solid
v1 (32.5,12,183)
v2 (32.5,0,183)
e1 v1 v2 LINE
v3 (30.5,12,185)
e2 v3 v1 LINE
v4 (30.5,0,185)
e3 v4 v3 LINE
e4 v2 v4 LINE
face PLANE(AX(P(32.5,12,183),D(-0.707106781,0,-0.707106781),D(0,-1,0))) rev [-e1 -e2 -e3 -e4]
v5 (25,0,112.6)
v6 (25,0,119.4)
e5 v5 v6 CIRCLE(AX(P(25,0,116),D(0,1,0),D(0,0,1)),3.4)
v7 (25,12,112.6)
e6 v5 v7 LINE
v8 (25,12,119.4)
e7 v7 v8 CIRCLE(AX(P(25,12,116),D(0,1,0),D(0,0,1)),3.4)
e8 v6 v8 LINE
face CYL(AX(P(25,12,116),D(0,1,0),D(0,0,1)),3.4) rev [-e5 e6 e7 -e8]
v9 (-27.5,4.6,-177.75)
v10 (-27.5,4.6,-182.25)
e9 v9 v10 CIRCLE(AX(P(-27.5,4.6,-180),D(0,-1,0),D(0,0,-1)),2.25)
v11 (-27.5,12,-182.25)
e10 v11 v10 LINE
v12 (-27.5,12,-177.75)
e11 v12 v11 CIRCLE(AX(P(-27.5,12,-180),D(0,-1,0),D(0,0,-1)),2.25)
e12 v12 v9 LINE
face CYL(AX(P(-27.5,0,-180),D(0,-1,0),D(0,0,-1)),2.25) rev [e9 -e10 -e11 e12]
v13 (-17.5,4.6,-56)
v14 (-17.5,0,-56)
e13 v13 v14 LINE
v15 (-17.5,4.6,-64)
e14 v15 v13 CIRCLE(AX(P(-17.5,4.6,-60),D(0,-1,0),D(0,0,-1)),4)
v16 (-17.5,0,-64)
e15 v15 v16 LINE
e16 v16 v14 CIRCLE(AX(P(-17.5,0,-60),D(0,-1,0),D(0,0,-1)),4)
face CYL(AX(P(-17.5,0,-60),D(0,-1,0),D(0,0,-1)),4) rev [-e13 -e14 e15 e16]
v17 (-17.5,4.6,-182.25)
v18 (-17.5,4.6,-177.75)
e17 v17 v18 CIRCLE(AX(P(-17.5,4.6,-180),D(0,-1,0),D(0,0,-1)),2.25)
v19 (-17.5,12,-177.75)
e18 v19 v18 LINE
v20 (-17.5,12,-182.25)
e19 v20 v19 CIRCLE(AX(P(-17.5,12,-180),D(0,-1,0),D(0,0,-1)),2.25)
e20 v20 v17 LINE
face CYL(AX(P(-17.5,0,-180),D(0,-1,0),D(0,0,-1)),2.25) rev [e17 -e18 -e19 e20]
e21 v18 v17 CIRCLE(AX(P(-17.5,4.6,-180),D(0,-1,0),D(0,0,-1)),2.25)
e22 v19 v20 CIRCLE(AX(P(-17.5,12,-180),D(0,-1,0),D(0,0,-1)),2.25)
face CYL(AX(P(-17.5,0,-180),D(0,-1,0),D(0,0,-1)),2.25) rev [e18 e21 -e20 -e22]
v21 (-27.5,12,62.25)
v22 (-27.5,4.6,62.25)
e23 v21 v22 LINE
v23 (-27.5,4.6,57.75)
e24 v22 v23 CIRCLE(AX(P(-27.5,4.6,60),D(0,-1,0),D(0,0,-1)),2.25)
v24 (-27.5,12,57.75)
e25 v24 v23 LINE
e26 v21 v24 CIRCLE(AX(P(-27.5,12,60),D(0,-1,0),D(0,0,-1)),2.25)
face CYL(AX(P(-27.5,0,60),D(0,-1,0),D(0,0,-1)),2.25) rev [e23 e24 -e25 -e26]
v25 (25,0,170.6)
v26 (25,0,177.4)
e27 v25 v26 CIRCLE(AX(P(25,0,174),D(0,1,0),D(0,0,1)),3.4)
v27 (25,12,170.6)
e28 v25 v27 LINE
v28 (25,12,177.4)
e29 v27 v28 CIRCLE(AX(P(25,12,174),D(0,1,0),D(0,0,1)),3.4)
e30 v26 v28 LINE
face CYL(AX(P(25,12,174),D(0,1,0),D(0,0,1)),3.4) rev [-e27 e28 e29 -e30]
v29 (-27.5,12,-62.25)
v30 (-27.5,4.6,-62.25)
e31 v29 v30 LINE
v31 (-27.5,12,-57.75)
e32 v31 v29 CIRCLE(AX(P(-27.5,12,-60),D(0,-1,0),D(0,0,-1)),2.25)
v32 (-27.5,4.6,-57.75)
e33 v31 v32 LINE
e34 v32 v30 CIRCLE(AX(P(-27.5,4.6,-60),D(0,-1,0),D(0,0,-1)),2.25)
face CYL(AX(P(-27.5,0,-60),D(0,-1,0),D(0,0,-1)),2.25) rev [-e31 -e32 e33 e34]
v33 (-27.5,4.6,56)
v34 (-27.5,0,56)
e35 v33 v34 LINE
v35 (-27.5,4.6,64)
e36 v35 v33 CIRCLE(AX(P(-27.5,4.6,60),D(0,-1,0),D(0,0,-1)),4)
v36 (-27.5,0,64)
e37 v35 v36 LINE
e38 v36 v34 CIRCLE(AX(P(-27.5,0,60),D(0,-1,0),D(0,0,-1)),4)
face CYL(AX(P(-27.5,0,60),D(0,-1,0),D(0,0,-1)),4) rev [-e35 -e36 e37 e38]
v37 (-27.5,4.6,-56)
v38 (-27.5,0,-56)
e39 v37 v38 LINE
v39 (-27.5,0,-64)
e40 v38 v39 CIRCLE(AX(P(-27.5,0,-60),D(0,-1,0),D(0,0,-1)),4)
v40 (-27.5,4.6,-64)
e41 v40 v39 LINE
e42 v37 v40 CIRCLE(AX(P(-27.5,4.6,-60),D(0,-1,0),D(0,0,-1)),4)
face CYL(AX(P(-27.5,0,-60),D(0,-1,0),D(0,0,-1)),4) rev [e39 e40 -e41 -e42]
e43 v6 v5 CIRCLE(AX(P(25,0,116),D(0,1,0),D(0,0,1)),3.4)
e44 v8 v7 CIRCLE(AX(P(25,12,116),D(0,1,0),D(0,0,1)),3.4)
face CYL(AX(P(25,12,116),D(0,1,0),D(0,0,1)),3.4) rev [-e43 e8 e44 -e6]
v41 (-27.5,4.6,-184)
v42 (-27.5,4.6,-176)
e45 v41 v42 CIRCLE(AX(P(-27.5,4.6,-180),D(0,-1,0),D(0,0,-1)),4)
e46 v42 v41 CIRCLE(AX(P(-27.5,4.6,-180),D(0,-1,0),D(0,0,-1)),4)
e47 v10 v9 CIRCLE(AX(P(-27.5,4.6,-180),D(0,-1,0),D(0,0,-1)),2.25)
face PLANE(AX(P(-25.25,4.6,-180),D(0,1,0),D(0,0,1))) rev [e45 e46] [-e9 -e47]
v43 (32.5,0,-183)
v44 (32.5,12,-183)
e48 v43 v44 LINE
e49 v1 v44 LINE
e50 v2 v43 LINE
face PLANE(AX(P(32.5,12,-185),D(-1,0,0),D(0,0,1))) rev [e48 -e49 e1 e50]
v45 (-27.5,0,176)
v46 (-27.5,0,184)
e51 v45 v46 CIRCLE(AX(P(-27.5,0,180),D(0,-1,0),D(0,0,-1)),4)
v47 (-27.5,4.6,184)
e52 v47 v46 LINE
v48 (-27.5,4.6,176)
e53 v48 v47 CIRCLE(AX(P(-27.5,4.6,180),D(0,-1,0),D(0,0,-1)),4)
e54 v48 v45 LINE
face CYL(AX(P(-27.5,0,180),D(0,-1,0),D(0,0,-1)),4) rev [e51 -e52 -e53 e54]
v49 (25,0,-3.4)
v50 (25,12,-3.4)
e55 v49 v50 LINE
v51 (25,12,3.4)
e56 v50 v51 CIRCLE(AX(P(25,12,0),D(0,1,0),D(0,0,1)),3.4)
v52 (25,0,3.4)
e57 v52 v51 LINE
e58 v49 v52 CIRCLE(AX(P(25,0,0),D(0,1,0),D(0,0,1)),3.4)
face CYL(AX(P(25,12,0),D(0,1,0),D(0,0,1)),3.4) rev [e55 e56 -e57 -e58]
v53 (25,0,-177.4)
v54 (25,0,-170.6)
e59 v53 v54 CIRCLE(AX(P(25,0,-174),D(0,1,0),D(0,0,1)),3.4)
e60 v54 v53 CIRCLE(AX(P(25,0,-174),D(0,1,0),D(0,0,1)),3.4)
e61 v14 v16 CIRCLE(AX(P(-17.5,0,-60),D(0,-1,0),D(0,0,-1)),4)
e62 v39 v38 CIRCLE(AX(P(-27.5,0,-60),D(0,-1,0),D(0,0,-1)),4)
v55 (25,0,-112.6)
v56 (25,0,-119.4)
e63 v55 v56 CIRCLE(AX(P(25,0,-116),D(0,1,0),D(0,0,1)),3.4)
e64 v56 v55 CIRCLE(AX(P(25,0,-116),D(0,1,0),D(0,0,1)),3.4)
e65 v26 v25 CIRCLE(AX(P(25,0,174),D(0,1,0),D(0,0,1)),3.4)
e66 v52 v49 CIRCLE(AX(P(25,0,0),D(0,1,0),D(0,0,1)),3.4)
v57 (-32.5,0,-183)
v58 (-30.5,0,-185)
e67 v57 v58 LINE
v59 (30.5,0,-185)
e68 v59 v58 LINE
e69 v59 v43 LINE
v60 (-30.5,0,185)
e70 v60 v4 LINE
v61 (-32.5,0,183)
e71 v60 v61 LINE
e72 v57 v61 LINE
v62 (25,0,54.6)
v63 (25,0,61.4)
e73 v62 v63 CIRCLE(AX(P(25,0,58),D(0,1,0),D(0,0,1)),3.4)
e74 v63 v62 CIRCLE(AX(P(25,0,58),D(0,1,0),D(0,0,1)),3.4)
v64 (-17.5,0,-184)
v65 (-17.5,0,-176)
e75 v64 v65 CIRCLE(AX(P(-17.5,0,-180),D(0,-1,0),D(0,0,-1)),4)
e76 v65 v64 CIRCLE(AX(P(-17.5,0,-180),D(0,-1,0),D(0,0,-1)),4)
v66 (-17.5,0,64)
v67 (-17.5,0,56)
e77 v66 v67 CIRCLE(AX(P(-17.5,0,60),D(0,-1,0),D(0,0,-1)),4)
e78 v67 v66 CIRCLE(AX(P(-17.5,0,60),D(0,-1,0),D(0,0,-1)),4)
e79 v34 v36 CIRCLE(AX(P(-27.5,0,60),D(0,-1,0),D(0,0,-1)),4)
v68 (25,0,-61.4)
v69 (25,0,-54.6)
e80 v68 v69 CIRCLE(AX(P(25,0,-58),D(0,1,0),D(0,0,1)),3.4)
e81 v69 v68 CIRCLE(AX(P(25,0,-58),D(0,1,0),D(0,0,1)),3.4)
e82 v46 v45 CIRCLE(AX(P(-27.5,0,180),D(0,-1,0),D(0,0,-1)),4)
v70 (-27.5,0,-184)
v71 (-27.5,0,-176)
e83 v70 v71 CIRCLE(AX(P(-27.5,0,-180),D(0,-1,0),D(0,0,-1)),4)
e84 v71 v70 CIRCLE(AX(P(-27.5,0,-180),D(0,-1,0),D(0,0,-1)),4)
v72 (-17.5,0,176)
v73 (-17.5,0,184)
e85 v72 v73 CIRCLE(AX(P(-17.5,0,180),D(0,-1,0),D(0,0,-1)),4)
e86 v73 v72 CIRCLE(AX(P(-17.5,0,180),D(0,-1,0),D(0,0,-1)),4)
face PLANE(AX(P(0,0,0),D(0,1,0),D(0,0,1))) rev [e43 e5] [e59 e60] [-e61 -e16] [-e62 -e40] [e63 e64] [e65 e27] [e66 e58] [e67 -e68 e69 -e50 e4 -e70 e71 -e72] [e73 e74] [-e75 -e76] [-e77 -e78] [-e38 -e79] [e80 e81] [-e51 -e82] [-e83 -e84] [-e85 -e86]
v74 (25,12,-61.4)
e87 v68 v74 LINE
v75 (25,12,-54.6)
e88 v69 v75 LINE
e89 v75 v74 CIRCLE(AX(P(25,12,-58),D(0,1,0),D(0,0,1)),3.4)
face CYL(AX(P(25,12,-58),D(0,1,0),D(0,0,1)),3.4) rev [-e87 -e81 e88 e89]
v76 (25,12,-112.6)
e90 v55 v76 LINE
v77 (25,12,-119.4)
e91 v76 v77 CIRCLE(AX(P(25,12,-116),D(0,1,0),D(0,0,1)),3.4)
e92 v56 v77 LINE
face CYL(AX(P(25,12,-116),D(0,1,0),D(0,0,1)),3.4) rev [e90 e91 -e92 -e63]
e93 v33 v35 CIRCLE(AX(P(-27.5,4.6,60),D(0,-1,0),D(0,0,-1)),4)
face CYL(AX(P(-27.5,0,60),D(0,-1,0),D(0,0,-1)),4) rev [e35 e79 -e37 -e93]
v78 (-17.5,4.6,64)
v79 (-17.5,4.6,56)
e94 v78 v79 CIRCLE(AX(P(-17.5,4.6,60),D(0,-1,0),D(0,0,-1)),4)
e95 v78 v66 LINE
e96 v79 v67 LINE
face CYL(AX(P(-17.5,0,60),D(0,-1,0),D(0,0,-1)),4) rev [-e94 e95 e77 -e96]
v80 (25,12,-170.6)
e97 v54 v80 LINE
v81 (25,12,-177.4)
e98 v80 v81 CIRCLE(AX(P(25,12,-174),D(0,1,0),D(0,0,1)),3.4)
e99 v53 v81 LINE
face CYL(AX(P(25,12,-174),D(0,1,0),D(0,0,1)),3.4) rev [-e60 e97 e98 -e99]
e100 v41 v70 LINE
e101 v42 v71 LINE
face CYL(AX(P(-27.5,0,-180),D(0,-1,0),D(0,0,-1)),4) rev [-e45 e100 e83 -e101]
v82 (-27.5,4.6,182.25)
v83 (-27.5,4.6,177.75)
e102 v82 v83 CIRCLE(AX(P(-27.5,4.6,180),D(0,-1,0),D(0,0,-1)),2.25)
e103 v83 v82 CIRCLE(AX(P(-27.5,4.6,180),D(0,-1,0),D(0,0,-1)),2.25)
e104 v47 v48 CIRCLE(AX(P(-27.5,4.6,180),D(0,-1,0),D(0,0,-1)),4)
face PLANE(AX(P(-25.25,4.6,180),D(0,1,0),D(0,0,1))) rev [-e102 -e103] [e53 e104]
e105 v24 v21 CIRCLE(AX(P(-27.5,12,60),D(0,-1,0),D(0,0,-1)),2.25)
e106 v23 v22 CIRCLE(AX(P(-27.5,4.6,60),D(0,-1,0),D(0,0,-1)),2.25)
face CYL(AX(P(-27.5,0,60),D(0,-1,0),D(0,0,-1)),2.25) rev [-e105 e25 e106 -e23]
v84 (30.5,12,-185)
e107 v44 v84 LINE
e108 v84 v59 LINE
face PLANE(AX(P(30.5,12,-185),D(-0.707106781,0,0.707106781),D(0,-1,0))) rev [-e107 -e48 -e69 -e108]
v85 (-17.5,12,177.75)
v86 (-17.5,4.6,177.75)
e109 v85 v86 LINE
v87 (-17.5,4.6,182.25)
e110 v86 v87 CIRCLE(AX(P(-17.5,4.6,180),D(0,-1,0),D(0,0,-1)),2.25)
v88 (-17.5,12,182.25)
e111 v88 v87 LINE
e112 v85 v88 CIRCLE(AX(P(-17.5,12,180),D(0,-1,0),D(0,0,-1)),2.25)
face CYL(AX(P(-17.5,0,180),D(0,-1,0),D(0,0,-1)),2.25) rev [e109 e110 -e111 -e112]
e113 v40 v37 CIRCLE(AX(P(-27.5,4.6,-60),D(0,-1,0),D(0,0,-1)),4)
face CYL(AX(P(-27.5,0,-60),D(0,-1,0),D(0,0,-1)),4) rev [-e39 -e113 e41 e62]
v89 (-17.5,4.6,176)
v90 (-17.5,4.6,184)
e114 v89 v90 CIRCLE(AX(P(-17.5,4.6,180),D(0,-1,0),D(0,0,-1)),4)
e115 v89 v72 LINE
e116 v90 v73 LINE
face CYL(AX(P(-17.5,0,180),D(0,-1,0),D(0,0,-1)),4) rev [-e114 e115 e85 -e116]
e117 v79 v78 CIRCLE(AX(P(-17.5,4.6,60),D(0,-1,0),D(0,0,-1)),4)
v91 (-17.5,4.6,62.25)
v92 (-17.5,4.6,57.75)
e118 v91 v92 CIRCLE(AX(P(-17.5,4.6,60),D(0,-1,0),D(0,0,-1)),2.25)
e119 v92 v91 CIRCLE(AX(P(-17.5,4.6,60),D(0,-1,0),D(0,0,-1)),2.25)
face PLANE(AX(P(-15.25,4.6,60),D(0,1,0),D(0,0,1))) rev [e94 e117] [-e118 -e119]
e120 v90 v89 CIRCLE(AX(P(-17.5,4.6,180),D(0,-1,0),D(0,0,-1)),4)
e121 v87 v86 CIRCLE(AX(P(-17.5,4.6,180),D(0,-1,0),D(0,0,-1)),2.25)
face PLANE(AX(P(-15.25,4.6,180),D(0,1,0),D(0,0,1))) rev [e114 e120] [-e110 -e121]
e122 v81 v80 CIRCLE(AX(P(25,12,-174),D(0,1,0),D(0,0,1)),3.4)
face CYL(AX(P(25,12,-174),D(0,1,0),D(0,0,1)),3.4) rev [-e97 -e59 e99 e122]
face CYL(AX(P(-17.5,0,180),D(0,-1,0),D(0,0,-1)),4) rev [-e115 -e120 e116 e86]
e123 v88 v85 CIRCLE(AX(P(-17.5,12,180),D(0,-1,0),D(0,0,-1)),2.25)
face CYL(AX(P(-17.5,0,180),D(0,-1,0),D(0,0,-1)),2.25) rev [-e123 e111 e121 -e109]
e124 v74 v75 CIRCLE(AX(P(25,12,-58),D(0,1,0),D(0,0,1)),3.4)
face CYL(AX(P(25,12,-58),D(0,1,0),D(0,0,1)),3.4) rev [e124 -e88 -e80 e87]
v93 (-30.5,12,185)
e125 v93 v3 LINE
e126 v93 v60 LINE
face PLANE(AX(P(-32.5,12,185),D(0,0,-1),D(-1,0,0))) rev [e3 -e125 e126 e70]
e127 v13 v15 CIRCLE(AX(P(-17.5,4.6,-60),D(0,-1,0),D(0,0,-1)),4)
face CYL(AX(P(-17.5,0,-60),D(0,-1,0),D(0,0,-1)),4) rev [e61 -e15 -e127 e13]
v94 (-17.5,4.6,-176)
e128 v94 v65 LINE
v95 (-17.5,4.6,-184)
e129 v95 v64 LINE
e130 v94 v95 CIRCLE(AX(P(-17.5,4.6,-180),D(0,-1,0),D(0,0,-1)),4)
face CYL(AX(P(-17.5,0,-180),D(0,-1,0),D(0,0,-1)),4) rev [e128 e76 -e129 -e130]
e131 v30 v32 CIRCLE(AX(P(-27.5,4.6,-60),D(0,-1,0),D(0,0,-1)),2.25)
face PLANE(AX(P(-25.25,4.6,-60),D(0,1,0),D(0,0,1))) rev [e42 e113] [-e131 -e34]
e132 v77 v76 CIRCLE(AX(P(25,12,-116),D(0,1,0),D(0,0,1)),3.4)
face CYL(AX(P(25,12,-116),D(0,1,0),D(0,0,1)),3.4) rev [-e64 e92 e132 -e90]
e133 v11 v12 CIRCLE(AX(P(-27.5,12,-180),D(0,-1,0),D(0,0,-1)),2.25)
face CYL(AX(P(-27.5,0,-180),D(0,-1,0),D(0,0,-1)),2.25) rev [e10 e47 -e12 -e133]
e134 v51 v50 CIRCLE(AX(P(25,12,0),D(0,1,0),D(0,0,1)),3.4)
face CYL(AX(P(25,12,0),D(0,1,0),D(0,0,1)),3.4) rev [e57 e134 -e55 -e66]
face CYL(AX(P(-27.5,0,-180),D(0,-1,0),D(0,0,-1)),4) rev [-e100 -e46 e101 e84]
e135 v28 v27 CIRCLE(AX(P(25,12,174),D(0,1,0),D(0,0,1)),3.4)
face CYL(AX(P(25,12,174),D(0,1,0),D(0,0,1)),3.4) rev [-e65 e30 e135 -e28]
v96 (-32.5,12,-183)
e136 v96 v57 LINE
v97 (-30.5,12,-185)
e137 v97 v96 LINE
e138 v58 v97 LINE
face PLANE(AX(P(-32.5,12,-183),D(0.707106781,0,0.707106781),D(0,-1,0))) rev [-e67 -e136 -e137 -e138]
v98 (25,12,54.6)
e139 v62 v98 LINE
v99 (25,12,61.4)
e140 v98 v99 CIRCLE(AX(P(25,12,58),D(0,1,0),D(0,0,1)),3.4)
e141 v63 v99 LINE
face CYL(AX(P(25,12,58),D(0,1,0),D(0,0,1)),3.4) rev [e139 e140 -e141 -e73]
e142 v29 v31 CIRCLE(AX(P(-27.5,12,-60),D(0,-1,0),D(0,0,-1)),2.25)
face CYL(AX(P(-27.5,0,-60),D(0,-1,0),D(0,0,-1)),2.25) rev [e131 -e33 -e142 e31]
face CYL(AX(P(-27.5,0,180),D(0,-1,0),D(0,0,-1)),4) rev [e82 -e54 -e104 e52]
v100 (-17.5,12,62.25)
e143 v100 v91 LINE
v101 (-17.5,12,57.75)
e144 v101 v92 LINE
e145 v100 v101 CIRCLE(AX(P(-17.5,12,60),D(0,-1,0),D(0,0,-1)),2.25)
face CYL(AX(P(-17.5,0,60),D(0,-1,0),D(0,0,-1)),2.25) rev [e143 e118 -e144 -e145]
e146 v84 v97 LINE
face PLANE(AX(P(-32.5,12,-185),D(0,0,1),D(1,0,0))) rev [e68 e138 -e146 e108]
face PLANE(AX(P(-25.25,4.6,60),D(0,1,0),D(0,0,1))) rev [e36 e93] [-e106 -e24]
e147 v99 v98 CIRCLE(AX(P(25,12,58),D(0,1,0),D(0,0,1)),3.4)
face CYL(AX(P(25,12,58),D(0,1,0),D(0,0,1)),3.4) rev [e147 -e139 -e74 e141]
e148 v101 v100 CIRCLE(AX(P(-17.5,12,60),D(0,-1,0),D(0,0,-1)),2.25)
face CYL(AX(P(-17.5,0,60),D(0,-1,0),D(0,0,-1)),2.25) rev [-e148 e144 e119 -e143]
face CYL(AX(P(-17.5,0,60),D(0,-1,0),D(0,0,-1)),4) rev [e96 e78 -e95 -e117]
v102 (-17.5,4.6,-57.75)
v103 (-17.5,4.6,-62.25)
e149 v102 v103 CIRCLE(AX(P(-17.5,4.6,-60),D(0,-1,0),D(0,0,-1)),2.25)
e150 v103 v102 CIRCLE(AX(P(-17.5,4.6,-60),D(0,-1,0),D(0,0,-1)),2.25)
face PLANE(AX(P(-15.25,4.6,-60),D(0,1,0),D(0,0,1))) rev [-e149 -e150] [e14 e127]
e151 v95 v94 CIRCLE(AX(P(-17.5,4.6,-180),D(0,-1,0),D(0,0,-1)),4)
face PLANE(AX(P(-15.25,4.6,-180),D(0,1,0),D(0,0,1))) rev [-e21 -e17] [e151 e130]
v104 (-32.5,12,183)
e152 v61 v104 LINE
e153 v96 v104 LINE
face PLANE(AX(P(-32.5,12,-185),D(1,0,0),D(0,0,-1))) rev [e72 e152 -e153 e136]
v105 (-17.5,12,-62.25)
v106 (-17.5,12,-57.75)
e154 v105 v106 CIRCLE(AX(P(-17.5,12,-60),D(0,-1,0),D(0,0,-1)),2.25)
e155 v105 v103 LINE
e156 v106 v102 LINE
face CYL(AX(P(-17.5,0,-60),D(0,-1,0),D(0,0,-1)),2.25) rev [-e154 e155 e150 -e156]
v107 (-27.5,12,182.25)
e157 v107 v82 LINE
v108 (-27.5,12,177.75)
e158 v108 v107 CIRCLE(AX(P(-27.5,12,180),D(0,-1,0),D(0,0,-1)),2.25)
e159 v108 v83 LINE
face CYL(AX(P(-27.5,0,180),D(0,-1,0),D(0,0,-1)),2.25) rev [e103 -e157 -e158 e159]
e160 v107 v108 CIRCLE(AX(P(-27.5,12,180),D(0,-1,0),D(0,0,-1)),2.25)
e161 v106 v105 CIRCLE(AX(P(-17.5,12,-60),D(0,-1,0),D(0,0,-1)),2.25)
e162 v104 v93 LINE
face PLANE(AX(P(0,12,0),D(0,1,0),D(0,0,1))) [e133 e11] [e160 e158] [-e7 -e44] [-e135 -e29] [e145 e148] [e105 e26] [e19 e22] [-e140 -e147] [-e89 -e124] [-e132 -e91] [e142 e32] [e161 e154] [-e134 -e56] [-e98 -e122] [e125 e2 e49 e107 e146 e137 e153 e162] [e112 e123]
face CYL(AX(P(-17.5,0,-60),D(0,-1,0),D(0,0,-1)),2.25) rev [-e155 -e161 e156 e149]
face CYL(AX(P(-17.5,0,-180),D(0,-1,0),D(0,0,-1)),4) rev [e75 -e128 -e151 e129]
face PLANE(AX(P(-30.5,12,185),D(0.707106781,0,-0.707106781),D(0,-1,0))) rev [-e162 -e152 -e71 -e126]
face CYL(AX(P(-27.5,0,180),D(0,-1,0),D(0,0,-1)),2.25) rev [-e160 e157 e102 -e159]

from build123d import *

# Parameters (mm, degrees)
SKETCH_1_W                = 65
SKETCH_1_H                = 370
EXTRUDE_1_DEPTH           = 12
HOLE_WIZARD_M8_1_D        = 6.8
HOLE_WIZARD_1_D           = 4.5
HOLE_WIZARD_1_CBORE_D     = 8
HOLE_WIZARD_1_CBORE_DEPTH = 4.6
CHAMFER_1_SIZE            = 2
PATTERN_LINEAR_1_COUNT    = 2
PATTERN_LINEAR_1_PITCH    = 10


with BuildPart() as part:
    # 草图1 → 凸台-拉伸1 (new body)
    with BuildSketch(Plane(origin=(0, 0, 0), x_dir=(1, 0, 0), z_dir=(0, 1, 0))):
        Rectangle(SKETCH_1_W, SKETCH_1_H)
    extrude(amount=EXTRUDE_1_DEPTH)

    # M8 螺纹孔1 (through all)
    with Locations(Plane(origin=(0, 12, 0), x_dir=(1, 0, 0), z_dir=(0, 1, 0))):
        with Locations((25, -174), (25, -116), (25, -58), (25, 0), (25, 58), (25, 116), (25, 174)):
            Hole(HOLE_WIZARD_M8_1_D / 2)

    # 打孔尺寸(%根据)内六角圆柱头螺钉的类型1 (through all)
    with Locations(Plane(origin=(0, 0, 0), x_dir=(-1, 0, 0), z_dir=(0, -1, 0))):
        with Locations((27.5, -180), (27.5, -60), (27.5, 60), (27.5, 180)):
            hole_wizard_1 = CounterBoreHole(HOLE_WIZARD_1_D / 2, HOLE_WIZARD_1_CBORE_D / 2, HOLE_WIZARD_1_CBORE_DEPTH)

    # 倒角1
    chamfer_1_edges = [part.edges().sort_by_distance(p)[0] for p in [
        (32.5, 6, 185),
        (-32.5, 6, 185),
        (-32.5, 6, -185),
        (32.5, 6, -185),
    ]]
    chamfer(chamfer_1_edges, length=CHAMFER_1_SIZE)

    # 阵列(线性)1: 打孔尺寸(%根据)内六角圆柱头螺钉的类型1 ×2
    with Locations(*[(i * PATTERN_LINEAR_1_PITCH, 0, 0) for i in range(1, PATTERN_LINEAR_1_COUNT)]):
        add(hole_wizard_1, mode=Mode.SUBTRACT)


solid = part.part
